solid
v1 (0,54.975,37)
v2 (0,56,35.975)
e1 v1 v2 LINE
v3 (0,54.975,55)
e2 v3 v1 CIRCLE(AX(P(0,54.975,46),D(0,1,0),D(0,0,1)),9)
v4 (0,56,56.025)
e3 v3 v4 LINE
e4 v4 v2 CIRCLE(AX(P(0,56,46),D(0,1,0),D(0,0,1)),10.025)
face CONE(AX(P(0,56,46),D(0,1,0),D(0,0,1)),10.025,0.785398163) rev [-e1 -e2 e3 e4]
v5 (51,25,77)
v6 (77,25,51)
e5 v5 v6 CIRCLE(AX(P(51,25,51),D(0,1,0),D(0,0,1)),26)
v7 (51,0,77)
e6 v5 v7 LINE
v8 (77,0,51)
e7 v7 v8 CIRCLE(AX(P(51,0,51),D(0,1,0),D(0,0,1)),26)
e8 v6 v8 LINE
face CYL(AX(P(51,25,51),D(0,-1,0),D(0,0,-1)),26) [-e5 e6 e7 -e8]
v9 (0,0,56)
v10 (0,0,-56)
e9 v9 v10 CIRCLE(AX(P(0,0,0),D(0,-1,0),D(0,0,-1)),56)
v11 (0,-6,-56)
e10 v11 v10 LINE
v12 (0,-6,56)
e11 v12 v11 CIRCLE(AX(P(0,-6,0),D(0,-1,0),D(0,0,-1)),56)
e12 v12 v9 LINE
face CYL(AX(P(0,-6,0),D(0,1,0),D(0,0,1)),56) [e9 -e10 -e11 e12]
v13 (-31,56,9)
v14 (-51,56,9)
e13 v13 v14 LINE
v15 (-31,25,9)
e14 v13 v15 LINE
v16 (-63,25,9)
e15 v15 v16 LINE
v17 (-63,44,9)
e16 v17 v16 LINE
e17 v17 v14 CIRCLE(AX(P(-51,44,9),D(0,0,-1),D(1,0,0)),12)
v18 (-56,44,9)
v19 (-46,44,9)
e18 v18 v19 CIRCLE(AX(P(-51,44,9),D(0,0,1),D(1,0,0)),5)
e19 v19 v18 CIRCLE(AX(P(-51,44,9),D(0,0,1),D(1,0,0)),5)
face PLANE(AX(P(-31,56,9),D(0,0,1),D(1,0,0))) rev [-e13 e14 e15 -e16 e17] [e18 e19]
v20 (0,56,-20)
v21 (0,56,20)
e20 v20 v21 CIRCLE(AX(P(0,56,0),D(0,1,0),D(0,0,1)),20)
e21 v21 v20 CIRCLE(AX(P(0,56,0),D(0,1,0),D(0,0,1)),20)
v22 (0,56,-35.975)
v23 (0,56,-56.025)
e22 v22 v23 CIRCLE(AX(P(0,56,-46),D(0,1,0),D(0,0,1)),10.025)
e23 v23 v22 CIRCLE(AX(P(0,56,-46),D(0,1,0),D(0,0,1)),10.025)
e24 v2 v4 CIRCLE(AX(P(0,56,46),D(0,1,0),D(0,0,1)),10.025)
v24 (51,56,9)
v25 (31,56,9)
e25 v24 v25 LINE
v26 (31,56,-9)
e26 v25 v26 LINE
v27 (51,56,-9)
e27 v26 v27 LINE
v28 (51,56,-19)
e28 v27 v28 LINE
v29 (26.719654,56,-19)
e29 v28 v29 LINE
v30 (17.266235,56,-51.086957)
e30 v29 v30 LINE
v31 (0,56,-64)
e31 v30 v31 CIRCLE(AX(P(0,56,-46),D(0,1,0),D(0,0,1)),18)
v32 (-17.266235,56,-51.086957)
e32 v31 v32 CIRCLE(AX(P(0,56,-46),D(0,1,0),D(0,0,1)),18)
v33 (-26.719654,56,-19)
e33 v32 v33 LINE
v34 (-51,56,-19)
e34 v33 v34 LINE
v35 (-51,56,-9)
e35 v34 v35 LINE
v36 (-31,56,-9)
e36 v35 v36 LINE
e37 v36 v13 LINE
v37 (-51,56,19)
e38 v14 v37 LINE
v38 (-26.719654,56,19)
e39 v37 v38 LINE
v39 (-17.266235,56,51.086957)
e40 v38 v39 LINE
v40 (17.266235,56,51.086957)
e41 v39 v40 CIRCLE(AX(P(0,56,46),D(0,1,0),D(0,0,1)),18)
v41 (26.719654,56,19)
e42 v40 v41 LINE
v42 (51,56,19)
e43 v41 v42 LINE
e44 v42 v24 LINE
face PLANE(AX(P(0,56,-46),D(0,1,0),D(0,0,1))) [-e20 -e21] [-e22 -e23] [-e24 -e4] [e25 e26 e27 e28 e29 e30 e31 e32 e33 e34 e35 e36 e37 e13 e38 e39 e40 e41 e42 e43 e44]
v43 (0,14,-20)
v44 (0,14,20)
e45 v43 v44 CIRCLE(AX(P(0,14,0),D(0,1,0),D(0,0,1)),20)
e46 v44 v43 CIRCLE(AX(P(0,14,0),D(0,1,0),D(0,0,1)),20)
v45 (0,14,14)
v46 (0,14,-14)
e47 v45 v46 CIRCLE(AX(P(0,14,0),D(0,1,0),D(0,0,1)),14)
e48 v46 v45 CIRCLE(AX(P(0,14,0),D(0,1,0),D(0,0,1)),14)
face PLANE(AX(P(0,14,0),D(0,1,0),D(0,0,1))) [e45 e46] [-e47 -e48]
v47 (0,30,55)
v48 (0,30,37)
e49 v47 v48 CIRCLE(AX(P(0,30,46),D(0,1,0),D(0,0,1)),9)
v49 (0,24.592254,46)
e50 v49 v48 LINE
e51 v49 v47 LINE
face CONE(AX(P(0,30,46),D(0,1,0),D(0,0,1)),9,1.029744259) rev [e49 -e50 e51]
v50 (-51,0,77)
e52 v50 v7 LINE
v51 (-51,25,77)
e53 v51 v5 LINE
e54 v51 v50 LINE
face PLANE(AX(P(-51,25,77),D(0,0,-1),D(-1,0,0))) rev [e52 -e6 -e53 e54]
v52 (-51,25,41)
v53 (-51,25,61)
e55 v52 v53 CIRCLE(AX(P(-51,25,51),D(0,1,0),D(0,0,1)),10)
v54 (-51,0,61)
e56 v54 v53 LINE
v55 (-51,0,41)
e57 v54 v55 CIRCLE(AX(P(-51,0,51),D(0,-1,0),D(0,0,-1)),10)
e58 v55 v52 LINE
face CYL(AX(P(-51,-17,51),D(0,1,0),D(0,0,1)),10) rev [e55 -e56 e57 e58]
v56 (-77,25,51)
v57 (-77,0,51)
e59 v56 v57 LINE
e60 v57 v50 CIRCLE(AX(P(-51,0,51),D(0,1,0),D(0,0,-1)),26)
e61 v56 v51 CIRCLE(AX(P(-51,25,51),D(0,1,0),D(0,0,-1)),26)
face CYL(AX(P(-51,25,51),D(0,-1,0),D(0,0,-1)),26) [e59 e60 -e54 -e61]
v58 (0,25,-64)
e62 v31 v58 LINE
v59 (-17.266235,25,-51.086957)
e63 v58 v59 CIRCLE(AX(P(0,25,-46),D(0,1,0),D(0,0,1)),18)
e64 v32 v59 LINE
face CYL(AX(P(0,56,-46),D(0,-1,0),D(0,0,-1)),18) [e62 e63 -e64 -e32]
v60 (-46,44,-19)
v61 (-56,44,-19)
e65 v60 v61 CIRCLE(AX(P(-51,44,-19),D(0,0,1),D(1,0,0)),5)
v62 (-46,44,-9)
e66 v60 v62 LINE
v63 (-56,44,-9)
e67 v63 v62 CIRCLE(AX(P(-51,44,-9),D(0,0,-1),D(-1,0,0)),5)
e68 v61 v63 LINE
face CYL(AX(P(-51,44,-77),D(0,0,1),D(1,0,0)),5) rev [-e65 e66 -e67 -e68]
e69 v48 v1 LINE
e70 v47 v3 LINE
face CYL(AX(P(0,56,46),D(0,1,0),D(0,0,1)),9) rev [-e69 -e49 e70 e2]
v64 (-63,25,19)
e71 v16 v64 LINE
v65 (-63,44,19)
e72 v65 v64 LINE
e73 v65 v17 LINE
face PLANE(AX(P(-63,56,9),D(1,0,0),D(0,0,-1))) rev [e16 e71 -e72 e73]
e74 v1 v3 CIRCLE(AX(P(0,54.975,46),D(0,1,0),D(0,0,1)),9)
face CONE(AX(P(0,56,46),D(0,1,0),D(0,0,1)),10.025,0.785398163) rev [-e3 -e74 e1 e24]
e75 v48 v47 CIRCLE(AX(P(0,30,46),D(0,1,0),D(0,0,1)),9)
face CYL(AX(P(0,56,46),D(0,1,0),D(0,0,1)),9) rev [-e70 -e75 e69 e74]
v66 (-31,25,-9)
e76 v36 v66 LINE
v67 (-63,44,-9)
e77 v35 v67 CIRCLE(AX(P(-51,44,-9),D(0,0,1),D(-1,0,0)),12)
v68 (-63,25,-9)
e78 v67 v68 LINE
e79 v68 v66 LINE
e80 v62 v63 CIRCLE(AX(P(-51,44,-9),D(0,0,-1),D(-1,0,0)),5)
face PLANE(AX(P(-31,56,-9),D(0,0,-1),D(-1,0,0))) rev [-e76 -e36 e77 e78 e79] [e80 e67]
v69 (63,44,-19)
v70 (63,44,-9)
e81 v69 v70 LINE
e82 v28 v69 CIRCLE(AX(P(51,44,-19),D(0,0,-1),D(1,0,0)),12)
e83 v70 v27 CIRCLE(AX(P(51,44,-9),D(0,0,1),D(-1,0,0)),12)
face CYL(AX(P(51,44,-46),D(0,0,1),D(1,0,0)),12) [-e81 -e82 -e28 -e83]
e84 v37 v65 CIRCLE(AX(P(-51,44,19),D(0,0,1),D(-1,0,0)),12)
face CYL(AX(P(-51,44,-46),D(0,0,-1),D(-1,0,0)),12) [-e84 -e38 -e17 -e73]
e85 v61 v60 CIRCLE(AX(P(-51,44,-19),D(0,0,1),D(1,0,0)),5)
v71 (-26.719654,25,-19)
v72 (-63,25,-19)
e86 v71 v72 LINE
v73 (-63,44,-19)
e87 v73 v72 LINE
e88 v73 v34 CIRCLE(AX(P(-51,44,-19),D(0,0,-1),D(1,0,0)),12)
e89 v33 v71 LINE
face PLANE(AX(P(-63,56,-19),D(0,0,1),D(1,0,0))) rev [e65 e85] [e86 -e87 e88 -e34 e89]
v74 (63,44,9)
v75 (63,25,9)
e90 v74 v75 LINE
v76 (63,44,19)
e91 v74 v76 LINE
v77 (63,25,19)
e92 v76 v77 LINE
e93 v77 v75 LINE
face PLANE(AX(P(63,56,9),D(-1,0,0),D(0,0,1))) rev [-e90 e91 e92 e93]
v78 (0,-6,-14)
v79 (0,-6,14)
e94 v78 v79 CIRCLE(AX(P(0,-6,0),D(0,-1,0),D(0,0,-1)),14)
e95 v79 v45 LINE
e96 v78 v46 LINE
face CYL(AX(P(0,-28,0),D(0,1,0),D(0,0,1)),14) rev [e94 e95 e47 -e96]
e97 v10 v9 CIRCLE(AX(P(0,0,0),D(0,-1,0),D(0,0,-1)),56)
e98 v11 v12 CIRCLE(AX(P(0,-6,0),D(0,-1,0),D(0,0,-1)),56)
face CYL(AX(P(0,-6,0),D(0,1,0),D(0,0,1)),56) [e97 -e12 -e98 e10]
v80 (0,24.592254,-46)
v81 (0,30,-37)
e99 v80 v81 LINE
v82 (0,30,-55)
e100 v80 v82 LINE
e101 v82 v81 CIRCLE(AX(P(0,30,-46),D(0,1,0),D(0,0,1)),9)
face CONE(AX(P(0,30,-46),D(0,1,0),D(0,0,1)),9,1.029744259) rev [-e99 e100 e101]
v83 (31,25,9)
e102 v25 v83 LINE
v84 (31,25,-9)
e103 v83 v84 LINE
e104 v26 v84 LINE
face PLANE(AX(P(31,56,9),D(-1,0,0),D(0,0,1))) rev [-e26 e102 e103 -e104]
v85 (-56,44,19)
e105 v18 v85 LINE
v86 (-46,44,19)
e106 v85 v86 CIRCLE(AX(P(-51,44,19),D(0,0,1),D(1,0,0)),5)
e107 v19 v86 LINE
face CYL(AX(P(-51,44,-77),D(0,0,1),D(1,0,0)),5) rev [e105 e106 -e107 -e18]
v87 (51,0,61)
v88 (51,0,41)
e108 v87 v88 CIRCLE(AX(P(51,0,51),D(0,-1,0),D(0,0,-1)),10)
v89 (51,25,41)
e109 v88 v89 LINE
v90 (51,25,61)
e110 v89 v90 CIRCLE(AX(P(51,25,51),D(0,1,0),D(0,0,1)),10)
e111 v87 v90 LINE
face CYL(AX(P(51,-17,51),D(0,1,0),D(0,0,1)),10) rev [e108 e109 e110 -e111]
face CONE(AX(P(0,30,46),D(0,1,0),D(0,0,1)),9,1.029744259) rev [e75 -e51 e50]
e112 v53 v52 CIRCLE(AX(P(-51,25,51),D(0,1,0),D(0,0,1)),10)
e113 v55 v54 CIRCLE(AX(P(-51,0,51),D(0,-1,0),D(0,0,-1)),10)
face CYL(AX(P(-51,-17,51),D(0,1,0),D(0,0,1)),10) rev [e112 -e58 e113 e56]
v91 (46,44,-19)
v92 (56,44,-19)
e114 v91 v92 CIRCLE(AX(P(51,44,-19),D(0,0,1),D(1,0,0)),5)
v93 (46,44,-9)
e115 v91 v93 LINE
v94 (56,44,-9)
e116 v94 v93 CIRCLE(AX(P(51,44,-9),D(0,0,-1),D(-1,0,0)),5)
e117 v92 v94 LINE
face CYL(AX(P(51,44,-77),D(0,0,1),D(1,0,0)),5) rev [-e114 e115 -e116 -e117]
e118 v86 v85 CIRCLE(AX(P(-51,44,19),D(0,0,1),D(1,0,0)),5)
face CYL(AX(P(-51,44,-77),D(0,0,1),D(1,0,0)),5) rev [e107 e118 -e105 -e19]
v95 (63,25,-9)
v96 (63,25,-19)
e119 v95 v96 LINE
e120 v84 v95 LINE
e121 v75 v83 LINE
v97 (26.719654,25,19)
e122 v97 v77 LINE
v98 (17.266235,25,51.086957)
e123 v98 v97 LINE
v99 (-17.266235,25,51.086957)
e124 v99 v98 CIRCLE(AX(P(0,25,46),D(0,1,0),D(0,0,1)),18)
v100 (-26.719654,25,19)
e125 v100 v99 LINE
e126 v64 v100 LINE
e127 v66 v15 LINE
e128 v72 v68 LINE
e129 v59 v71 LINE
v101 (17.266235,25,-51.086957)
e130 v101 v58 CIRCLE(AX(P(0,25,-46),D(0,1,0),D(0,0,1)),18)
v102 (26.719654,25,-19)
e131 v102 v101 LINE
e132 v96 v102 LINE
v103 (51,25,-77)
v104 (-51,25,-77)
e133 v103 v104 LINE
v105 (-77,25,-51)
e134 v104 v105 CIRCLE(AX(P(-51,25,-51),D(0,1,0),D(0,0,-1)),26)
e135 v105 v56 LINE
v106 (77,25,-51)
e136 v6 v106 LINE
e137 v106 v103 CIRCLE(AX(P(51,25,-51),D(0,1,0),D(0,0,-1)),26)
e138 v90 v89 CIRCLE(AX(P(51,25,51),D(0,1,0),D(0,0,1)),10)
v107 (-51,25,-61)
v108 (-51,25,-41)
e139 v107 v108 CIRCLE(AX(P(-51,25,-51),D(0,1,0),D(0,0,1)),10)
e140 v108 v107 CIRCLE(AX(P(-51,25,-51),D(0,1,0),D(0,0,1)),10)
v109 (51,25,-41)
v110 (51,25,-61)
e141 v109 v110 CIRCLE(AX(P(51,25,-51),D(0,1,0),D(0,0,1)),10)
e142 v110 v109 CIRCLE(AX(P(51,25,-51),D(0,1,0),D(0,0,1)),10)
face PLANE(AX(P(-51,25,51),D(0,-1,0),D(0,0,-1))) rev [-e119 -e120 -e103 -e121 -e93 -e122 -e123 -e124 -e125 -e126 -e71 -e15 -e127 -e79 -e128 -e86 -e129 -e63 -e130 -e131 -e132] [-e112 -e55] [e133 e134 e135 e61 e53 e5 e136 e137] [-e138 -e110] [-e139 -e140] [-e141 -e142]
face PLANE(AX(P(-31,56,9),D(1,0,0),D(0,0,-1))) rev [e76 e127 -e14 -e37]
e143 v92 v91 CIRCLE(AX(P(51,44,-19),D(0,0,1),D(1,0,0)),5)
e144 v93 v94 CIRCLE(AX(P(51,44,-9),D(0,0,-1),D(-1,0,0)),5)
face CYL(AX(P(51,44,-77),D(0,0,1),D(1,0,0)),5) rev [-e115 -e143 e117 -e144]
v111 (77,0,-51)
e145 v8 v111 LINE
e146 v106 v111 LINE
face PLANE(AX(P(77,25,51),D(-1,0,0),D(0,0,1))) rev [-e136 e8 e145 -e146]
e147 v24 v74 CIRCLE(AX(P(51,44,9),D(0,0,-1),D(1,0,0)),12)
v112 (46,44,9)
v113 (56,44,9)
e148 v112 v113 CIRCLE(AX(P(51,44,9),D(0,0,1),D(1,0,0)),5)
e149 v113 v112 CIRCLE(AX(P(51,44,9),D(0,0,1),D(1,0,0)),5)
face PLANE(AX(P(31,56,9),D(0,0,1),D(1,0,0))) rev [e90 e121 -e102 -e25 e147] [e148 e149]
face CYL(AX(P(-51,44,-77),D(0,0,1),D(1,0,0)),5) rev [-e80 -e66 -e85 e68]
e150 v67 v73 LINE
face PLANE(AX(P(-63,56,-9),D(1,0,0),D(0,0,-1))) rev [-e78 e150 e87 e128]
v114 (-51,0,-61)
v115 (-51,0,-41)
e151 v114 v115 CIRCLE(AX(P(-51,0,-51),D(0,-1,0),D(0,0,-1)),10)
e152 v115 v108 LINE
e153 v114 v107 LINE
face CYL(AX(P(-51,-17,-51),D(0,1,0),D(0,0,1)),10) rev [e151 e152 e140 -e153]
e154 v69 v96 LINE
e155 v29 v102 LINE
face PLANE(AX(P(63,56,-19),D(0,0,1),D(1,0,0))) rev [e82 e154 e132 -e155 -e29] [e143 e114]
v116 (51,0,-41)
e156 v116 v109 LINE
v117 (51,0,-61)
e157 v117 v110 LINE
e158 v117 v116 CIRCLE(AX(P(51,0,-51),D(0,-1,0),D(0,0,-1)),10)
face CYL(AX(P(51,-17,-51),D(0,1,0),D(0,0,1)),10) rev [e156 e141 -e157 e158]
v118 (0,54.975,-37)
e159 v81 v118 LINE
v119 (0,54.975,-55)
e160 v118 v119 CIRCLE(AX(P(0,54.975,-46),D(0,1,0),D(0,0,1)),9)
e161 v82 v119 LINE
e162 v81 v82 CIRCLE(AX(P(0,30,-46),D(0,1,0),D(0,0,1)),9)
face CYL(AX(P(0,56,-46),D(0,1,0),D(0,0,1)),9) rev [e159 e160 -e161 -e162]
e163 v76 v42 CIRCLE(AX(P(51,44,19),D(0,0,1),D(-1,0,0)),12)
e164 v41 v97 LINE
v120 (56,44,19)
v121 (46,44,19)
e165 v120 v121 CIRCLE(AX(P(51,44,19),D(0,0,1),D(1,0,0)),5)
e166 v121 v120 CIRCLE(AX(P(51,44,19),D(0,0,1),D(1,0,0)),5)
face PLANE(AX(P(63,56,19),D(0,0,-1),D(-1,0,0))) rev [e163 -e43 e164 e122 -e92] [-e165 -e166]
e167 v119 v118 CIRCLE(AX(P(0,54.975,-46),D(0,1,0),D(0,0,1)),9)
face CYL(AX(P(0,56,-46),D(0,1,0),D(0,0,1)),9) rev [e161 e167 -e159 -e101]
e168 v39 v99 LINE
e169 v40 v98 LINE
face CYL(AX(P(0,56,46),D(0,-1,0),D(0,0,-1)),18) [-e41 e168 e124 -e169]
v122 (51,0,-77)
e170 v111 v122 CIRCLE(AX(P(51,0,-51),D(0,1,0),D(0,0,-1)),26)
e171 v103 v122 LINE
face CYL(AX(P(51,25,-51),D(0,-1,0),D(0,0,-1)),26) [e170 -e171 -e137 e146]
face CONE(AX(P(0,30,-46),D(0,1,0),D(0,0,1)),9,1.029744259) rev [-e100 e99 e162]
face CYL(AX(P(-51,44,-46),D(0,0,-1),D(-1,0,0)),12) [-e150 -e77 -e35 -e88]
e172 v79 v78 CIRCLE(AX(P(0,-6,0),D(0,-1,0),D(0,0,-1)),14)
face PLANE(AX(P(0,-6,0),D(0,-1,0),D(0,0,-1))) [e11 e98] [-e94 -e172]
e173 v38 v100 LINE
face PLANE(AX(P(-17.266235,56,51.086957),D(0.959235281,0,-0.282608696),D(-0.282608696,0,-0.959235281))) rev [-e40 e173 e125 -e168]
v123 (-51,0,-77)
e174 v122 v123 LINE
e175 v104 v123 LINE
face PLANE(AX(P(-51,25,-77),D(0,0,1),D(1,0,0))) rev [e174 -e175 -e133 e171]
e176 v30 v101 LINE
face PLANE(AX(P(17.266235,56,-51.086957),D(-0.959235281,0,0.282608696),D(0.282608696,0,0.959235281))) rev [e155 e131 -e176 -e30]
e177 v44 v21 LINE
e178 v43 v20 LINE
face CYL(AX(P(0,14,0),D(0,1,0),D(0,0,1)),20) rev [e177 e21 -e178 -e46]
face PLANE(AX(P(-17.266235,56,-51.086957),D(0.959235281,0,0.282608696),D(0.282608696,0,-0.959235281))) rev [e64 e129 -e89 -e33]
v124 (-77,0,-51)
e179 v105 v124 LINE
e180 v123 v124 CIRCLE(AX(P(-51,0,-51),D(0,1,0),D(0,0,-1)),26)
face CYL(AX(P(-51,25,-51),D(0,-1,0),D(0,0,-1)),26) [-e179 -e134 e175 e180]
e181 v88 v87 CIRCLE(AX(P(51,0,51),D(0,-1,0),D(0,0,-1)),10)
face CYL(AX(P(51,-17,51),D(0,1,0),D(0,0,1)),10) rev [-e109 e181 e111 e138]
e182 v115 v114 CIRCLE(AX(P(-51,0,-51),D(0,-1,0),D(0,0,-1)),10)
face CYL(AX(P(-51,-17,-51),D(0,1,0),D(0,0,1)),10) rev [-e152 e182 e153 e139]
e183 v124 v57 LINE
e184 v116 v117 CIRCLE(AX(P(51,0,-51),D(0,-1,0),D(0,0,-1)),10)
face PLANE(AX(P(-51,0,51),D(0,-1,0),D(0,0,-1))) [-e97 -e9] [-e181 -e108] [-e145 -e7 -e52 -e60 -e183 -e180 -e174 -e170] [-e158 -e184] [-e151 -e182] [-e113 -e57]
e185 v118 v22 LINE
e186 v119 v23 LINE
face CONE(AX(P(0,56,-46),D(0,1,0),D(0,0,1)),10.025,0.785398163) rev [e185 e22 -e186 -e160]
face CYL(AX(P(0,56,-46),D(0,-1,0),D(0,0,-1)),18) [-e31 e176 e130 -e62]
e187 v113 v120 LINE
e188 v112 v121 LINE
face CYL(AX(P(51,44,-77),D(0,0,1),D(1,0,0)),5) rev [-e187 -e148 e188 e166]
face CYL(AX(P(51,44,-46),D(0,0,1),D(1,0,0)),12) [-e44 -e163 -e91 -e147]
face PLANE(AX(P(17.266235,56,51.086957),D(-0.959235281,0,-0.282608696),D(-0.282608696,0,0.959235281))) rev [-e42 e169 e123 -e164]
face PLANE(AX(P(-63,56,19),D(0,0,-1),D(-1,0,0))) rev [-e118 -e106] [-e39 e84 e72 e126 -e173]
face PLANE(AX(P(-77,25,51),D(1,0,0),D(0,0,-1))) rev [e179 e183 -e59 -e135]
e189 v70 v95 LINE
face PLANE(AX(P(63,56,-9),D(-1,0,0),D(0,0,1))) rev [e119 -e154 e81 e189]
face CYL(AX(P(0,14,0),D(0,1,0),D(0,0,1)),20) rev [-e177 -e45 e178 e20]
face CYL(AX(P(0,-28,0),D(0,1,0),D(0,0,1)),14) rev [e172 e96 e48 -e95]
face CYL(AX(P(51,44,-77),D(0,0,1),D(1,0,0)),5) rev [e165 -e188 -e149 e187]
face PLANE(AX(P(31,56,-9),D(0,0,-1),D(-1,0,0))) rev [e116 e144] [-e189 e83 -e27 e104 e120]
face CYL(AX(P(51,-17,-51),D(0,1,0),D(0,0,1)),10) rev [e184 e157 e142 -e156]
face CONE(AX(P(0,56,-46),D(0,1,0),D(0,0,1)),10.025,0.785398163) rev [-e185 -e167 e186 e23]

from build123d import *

# Parameters (mm, degrees)
BASE_PLATE_154X154X25_DEPTH      = 25
LOCATING_SPIGOT_SKETCH_112_R     = 56
LOCATING_SPIGOT_112X6_DEPTH      = 6
PIVOT_BOSS_WITH_LUGS_DEPTH       = 31
PIVOT_BOSS_FILLETS_R12_R         = 12
LUG_PIN_HOLES_SKETCH_10_R        = 5
LUG_PIN_HOLES_10_DEPTH           = 136.207248326
CENTRE_BORE_SKETCH_40_R          = 20
CENTRE_BORE_40_DEPTH             = 42
THROUGH_BORE_SKETCH_28_R         = 14
THROUGH_BORE_28_DEPTH            = 42
TAPPED_HOLES_M20X2_0_D           = 18
TAPPED_HOLES_M20X2_0_DEPTH       = 26
TAPPED_HOLES_M20X2_0_CSINK_D     = 20.05
TAPPED_HOLES_M20X2_0_CSINK_ANGLE = 90
TAPPED_HOLES_M20X2_0_TIP         = 5.407745571
MOUNTING_HOLES_SKETCH_4X_20_R    = 10
MOUNTING_HOLES_4X_20_DEPTH       = 42


with BuildPart() as part:
    # Base Plate Profile 154x154 R26 → Base Plate 154x154x25 (new body)
    with BuildSketch(Plane(origin=(0, 0, 0), x_dir=(1, 0, 0), z_dir=(0, 1, 0))):
        with BuildLine():
            Line((-51, -77), (51, -77))
            ThreePointArc((51, -77), (69.384776311, -69.384776311), (77, -51))
            Line((77, -51), (77, 51))
            ThreePointArc((77, 51), (69.384776311, 69.384776311), (51, 77))
            Line((51, 77), (-51, 77))
            ThreePointArc((-51, 77), (-69.384776311, 69.384776311), (-77, 51))
            Line((-77, 51), (-77, -51))
            ThreePointArc((-77, -51), (-69.384776311, -69.384776311), (-51, -77))
        make_face()
    extrude(amount=BASE_PLATE_154X154X25_DEPTH)

    # Locating Spigot Sketch Ø112 → Locating Spigot Ø112x6 (add)
    with BuildSketch(Plane.XZ):
        with Locations(Location((0, 0, 0), (0, 0, 270))):
            Circle(LOCATING_SPIGOT_SKETCH_112_R)
    extrude(amount=LOCATING_SPIGOT_112X6_DEPTH)

    # Pivot Boss Profile → Pivot Boss with Lugs (add)
    with BuildSketch(Plane(origin=(0, 25, 0), x_dir=(1, 0, 0), z_dir=(0, 1, 0))):
        with BuildLine():
            Line((-17.266235066, 51.086956522), (-26.719653956, 19))
            Line((-26.719653956, 19), (-63, 19))
            Line((-63, 19), (-63, 9))
            Line((-63, 9), (-31, 9))
            Line((-31, 9), (-31, -9))
            Line((-31, -9), (-63, -9))
            Line((-63, -9), (-63, -19))
            Line((-63, -19), (-26.719653956, -19))
            Line((-26.719653956, -19), (-17.266235066, -51.086956522))
            ThreePointArc((-17.266235066, -51.086956522), (0, -64), (17.266235066, -51.086956522))
            Line((17.266235066, -51.086956522), (26.719653956, -19))
            Line((26.719653956, -19), (63, -19))
            Line((63, -19), (63, -9))
            Line((63, -9), (31, -9))
            Line((31, -9), (31, 9))
            Line((31, 9), (63, 9))
            Line((63, 9), (63, 19))
            Line((63, 19), (26.719653956, 19))
            Line((26.719653956, 19), (17.266235066, 51.086956522))
            ThreePointArc((17.266235066, 51.086956522), (0, 64), (-17.266235066, 51.086956522))
        make_face()
    extrude(amount=PIVOT_BOSS_WITH_LUGS_DEPTH)

    # Pivot Boss Fillets R12
    pivot_boss_fillets_r12_edges = [part.edges().sort_by_distance(p)[0] for p in [
        (-63, 56, 14),
        (63, 56, 14),
        (63, 56, -14),
        (-63, 56, -14),
    ]]
    fillet(pivot_boss_fillets_r12_edges, radius=PIVOT_BOSS_FILLETS_R12_R)

    # Lug Pin Holes Sketch Ø10 → Lug Pin Holes Ø10 (cut, through all)
    with BuildSketch(Plane.XY.offset(19)):
        with Locations((-51, 44)):
            Circle(LUG_PIN_HOLES_SKETCH_10_R)
        with Locations((51, 44)):
            Circle(LUG_PIN_HOLES_SKETCH_10_R)
    extrude(amount=-LUG_PIN_HOLES_10_DEPTH, mode=Mode.SUBTRACT)

    # Centre Bore Sketch Ø40 → Centre Bore Ø40 (cut)
    with BuildSketch(Plane(origin=(0, 56, 0), x_dir=(1, 0, 0), z_dir=(0, 1, 0))):
        with Locations(Location((0, 0, 0), (0, 0, 270))):
            Circle(CENTRE_BORE_SKETCH_40_R)
    extrude(amount=-CENTRE_BORE_40_DEPTH, mode=Mode.SUBTRACT)

    # Through Bore Sketch Ø28 → Through Bore Ø28 (cut)
    with BuildSketch(Plane(origin=(0, 14, 0), x_dir=(1, 0, 0), z_dir=(0, 1, 0))):
        with Locations(Location((0, 0, 0), (0, 0, 270))):
            Circle(THROUGH_BORE_SKETCH_28_R)
    extrude(amount=-THROUGH_BORE_28_DEPTH, mode=Mode.SUBTRACT)

    # Tapped Holes M20x2.0
    with Locations(Plane(origin=(0, 56, 0), x_dir=(1, 0, 0), z_dir=(0, 1, 0))):
        with Locations((0, 46), (0, -46)):
            CounterSinkHole(TAPPED_HOLES_M20X2_0_D / 2, TAPPED_HOLES_M20X2_0_CSINK_D / 2, depth=TAPPED_HOLES_M20X2_0_DEPTH, counter_sink_angle=TAPPED_HOLES_M20X2_0_CSINK_ANGLE)
            with Locations((0, 0, -(TAPPED_HOLES_M20X2_0_DEPTH + TAPPED_HOLES_M20X2_0_TIP / 2))):  # 118° drill point
                Cone(0, TAPPED_HOLES_M20X2_0_D / 2, TAPPED_HOLES_M20X2_0_TIP, mode=Mode.SUBTRACT)

    # Mounting Holes Sketch 4xØ20 → Mounting Holes 4xØ20 (cut)
    with BuildSketch(Plane(origin=(0, 25, 0), x_dir=(1, 0, 0), z_dir=(0, 1, 0))):
        with Locations(Location((51, 51, 0), (0, 0, 270))):
            Circle(MOUNTING_HOLES_SKETCH_4X_20_R)
        with Locations(Location((-51, 51, 0), (0, 0, 270))):
            Circle(MOUNTING_HOLES_SKETCH_4X_20_R)
        with Locations(Location((-51, -51, 0), (0, 0, 270))):
            Circle(MOUNTING_HOLES_SKETCH_4X_20_R)
        with Locations(Location((51, -51, 0), (0, 0, 270))):
            Circle(MOUNTING_HOLES_SKETCH_4X_20_R)
    extrude(amount=-MOUNTING_HOLES_4X_20_DEPTH, mode=Mode.SUBTRACT)


solid = part.part
